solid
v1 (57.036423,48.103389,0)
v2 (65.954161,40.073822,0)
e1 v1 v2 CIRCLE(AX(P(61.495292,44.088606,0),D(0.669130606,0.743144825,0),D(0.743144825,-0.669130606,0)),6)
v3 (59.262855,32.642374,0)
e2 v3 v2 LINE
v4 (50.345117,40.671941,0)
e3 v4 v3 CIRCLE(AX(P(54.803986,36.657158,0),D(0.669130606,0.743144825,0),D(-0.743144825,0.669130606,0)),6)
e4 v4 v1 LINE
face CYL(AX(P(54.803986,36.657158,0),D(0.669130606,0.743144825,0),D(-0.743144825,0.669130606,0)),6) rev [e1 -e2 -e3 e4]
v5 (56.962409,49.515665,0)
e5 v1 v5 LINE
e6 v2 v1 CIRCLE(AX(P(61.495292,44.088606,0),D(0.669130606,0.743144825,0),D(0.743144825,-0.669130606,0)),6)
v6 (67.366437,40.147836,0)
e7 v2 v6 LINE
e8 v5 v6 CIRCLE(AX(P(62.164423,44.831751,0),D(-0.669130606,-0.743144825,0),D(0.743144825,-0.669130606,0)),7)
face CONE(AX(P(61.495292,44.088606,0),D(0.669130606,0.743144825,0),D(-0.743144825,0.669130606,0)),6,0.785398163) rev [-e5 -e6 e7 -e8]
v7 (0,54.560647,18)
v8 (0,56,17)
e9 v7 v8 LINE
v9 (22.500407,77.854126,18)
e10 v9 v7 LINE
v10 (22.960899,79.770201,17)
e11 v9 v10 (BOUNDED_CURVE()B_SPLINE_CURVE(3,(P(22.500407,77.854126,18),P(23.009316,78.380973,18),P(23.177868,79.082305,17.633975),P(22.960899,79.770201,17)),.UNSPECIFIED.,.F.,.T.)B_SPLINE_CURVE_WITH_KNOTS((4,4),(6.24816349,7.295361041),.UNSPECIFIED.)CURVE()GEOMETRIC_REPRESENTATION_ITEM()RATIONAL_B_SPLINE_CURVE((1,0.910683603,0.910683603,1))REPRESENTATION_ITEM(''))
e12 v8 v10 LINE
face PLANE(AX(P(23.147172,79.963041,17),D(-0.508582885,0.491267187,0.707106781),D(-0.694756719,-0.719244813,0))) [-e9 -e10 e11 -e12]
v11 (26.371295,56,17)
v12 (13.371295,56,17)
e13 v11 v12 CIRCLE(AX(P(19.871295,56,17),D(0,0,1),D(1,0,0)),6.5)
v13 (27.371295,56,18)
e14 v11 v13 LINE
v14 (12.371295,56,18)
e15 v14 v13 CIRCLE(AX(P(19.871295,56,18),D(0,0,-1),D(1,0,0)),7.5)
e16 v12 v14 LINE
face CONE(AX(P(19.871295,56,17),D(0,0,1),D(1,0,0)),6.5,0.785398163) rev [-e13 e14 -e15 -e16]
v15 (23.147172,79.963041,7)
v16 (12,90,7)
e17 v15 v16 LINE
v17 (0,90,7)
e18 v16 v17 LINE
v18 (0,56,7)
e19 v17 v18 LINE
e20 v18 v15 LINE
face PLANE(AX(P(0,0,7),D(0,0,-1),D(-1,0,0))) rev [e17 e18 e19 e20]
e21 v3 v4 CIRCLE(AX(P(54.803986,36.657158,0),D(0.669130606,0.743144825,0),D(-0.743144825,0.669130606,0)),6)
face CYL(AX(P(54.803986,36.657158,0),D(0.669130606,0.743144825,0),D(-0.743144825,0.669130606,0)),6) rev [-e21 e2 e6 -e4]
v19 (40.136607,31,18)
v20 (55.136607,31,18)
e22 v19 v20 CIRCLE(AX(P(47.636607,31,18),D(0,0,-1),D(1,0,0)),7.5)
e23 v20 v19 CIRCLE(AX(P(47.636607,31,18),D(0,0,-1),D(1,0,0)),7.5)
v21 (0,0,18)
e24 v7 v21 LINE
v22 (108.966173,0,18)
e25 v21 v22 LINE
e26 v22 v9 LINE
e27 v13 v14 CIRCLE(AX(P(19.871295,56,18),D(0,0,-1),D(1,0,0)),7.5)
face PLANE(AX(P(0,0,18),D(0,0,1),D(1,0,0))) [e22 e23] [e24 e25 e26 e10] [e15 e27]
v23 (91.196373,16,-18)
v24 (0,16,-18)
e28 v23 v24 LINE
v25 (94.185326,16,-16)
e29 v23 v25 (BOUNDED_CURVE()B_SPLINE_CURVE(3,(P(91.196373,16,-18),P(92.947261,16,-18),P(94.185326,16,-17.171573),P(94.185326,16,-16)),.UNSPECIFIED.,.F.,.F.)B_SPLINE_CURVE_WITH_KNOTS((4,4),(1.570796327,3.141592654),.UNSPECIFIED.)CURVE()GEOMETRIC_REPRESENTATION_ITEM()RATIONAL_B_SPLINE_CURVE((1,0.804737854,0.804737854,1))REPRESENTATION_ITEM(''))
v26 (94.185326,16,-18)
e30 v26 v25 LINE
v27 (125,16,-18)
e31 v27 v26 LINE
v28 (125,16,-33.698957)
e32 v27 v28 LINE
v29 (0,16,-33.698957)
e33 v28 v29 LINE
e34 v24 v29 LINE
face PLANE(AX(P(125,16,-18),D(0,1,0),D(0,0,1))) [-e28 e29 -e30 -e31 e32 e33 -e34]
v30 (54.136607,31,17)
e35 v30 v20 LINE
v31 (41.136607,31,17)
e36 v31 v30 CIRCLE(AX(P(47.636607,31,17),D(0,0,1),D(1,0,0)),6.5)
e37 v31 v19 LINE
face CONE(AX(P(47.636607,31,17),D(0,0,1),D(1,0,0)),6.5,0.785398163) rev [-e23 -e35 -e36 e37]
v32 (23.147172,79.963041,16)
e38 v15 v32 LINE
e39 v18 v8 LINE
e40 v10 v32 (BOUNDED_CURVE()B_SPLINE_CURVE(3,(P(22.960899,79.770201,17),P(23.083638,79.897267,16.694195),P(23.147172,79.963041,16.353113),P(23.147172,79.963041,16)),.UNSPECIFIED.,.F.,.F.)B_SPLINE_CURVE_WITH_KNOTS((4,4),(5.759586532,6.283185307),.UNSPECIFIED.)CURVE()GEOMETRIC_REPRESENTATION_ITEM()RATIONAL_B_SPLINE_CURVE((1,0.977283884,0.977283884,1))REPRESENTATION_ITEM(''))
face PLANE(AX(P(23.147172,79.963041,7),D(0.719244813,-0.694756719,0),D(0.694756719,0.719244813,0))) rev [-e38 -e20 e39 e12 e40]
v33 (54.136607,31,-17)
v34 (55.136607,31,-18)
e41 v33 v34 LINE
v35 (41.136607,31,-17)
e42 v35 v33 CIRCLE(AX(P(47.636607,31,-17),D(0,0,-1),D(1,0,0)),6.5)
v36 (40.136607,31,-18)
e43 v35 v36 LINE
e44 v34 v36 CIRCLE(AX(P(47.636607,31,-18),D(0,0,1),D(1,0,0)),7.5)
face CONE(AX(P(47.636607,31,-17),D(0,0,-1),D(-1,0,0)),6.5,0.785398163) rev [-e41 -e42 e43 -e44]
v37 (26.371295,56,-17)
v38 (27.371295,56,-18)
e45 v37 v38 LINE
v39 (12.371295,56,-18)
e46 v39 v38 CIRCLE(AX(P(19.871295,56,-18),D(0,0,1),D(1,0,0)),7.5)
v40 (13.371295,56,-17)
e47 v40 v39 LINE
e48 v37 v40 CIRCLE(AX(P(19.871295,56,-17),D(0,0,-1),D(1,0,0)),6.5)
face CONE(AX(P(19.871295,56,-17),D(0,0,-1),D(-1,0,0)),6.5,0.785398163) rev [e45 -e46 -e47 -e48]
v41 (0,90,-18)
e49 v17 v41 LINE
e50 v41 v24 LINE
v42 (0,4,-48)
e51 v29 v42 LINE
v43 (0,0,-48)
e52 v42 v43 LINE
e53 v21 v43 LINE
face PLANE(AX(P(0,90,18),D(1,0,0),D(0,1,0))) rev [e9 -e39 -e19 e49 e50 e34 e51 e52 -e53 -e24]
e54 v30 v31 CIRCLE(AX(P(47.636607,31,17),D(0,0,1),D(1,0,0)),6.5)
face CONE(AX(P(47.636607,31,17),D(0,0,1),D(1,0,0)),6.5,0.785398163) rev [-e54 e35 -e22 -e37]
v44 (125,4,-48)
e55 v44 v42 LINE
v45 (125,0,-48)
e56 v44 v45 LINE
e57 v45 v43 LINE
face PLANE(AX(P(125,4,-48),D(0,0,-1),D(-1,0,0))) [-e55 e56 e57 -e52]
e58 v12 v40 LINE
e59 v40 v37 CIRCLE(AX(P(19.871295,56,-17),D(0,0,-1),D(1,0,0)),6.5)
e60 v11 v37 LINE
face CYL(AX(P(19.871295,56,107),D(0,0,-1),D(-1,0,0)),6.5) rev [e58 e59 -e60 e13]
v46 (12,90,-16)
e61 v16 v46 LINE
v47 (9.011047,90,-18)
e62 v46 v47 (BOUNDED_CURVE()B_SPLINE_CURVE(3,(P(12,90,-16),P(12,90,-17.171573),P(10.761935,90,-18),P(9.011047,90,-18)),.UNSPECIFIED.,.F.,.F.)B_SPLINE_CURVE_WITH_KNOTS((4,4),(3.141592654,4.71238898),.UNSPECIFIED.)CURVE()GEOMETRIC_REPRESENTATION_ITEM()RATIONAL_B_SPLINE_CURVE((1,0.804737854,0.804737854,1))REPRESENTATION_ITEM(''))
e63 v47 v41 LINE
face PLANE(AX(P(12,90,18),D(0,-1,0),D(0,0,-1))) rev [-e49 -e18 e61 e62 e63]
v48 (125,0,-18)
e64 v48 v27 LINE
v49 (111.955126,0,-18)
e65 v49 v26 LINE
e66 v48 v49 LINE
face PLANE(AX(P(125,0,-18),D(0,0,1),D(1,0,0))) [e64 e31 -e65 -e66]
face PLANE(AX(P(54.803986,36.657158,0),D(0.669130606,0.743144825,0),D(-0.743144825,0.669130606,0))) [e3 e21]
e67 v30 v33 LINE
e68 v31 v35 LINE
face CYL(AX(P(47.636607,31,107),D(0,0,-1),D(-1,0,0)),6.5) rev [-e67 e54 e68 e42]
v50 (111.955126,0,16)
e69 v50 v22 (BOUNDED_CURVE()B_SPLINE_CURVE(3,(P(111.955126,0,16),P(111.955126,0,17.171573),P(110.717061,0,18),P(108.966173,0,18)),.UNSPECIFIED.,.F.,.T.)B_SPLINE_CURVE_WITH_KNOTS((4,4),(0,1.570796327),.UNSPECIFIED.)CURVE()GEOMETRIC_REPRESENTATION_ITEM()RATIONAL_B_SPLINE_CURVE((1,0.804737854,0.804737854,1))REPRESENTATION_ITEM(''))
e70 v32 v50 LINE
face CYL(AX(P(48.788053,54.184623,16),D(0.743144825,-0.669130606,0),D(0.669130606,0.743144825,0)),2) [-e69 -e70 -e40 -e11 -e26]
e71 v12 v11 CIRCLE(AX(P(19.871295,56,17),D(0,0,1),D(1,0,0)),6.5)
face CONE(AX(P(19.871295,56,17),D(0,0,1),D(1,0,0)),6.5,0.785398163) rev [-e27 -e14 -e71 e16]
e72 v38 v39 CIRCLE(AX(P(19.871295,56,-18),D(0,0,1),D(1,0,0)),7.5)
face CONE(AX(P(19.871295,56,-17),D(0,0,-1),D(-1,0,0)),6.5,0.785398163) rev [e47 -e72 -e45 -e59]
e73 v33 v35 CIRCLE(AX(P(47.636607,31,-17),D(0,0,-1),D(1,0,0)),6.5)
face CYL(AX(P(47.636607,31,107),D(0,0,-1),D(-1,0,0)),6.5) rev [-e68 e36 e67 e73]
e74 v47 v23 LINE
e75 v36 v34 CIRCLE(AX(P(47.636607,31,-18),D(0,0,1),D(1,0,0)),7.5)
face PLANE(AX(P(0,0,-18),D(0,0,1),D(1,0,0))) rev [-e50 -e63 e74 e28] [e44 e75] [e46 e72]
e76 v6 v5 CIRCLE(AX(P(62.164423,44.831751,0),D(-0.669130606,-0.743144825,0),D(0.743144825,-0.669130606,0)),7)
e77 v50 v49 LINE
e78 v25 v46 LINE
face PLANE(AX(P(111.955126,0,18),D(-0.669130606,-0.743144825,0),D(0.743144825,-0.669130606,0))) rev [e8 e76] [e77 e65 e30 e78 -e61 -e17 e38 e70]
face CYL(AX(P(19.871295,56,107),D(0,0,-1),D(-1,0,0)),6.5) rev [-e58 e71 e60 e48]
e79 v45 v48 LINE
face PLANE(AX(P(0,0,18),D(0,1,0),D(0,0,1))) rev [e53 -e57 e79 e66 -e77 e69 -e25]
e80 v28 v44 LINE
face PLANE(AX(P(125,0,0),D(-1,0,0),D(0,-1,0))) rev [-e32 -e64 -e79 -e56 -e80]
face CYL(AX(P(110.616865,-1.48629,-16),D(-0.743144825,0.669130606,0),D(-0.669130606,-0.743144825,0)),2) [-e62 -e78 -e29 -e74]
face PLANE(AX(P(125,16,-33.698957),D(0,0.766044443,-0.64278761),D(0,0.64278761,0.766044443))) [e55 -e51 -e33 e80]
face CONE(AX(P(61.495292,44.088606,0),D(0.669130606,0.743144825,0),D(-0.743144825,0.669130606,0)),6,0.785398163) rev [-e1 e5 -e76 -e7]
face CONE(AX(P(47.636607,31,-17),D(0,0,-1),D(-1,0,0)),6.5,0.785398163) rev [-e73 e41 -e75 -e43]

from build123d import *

# Parameters (mm, degrees)
TRIANGULAR_BRACKET_BODY_DEPTH    = 18
RECTANGULAR_CUT_15X56_DEPTH      = 11
HOLE_SKETCH_R                    = 6
HOLE_CUT_DEPTH                   = 11
SLIDE_RAIL_125_DEPTH             = 125
RAIL_GROOVE_SKETCH_R             = 6.5
RAIL_GROOVE_CUT_DEPTH            = 125
RECTANGULAR_CUT_CHAMFER_1MM_SIZE = 1
HOLE_AND_GROOVE_CHAMFER_1MM_SIZE = 1
BODY_EDGE_FILLET_R2_A_R          = 2
BODY_EDGE_FILLET_R2_B_R          = 2


with BuildPart() as part:
    # Bracket Profile Sketch → Triangular Bracket Body (new, symmetric)
    with BuildSketch(Plane.XY):
        Polygon((0, 0), (111.955126335, 0), (12, 90), (0, 90), align=None)
    extrude(amount=TRIANGULAR_BRACKET_BODY_DEPTH, both=True)

    # Rectangular Cut Sketch → Rectangular Cut 15x56 (cut)
    with BuildSketch(Plane.XY.offset(18)):
        Polygon((23.147172382, 79.963040905), (0, 56), (0, 90), (12, 90), align=None)
    extrude(amount=-RECTANGULAR_CUT_15X56_DEPTH, mode=Mode.SUBTRACT)

    # Hole Sketch → Hole Cut (cut)
    with BuildSketch(Plane(origin=(50.126314512, 55.670912219, 0), x_dir=(0.743144825477398, -0.669130606358854, 0), z_dir=(0.669130606358854, 0.743144825477398, 0))):
        with Locations(Location((16.198872821, 0, 0), (0, 0, 180))):
            Circle(HOLE_SKETCH_R)
    extrude(amount=-HOLE_CUT_DEPTH, mode=Mode.SUBTRACT)

    # Slide Rail Profile Sketch → Slide Rail 125 (add)
    with BuildSketch(Plane.ZY):
        Polygon((-18, 16), (-33.698956889, 16), (-48, 4), (-48, 0), (-18, 0), align=None)
    extrude(amount=-SLIDE_RAIL_125_DEPTH)

    # Rail Groove Sketch → Rail Groove Cut (cut)
    with BuildSketch(Plane(origin=(0, 0, -18), x_dir=(-1, 0, 0), z_dir=(0, 0, -1))):
        with Locations((-47.636607378, 31)):
            Circle(RAIL_GROOVE_SKETCH_R)
        with Locations((-19.871294507, 56)):
            Circle(RAIL_GROOVE_SKETCH_R)
    extrude(amount=-RAIL_GROOVE_CUT_DEPTH, mode=Mode.SUBTRACT)

    # Rectangular Cut Chamfer 1mm
    rectangular_cut_chamfer_1mm_edges = [part.edges().sort_by_distance(p)[0] for p in [
        (11.573586191, 67.981520452, 18),
    ]]
    chamfer(rectangular_cut_chamfer_1mm_edges, length=RECTANGULAR_CUT_CHAMFER_1MM_SIZE)

    # Hole and Groove Chamfer 1mm
    hole_and_groove_chamfer_1mm_edges = [part.edges().sort_by_distance(p)[0] for p in [
        (66.623291981, 40.816966988, 0),
        (54.136607378, 31, 18),
        (54.136607378, 31, -18),
        (26.371294507, 56, 18),
        (26.371294507, 56, -18),
    ]]
    chamfer(hole_and_groove_chamfer_1mm_edges, length=HOLE_AND_GROOVE_CHAMFER_1MM_SIZE)

    # Body Edge Fillet R2 A
    body_edge_fillet_r2_a_edges = [part.edges().sort_by_distance(p)[0] for p in [
        (53.092663049, 53, -18),
    ]]
    fillet(body_edge_fillet_r2_a_edges, radius=BODY_EDGE_FILLET_R2_A_R)

    # Body Edge Fillet R2 B
    body_edge_fillet_r2_b_edges = [part.edges().sort_by_distance(p)[0] for p in [
        (67.92295004, 39.646749615, 18),
    ]]
    fillet(body_edge_fillet_r2_b_edges, radius=BODY_EDGE_FILLET_R2_B_R)


solid = part.part
